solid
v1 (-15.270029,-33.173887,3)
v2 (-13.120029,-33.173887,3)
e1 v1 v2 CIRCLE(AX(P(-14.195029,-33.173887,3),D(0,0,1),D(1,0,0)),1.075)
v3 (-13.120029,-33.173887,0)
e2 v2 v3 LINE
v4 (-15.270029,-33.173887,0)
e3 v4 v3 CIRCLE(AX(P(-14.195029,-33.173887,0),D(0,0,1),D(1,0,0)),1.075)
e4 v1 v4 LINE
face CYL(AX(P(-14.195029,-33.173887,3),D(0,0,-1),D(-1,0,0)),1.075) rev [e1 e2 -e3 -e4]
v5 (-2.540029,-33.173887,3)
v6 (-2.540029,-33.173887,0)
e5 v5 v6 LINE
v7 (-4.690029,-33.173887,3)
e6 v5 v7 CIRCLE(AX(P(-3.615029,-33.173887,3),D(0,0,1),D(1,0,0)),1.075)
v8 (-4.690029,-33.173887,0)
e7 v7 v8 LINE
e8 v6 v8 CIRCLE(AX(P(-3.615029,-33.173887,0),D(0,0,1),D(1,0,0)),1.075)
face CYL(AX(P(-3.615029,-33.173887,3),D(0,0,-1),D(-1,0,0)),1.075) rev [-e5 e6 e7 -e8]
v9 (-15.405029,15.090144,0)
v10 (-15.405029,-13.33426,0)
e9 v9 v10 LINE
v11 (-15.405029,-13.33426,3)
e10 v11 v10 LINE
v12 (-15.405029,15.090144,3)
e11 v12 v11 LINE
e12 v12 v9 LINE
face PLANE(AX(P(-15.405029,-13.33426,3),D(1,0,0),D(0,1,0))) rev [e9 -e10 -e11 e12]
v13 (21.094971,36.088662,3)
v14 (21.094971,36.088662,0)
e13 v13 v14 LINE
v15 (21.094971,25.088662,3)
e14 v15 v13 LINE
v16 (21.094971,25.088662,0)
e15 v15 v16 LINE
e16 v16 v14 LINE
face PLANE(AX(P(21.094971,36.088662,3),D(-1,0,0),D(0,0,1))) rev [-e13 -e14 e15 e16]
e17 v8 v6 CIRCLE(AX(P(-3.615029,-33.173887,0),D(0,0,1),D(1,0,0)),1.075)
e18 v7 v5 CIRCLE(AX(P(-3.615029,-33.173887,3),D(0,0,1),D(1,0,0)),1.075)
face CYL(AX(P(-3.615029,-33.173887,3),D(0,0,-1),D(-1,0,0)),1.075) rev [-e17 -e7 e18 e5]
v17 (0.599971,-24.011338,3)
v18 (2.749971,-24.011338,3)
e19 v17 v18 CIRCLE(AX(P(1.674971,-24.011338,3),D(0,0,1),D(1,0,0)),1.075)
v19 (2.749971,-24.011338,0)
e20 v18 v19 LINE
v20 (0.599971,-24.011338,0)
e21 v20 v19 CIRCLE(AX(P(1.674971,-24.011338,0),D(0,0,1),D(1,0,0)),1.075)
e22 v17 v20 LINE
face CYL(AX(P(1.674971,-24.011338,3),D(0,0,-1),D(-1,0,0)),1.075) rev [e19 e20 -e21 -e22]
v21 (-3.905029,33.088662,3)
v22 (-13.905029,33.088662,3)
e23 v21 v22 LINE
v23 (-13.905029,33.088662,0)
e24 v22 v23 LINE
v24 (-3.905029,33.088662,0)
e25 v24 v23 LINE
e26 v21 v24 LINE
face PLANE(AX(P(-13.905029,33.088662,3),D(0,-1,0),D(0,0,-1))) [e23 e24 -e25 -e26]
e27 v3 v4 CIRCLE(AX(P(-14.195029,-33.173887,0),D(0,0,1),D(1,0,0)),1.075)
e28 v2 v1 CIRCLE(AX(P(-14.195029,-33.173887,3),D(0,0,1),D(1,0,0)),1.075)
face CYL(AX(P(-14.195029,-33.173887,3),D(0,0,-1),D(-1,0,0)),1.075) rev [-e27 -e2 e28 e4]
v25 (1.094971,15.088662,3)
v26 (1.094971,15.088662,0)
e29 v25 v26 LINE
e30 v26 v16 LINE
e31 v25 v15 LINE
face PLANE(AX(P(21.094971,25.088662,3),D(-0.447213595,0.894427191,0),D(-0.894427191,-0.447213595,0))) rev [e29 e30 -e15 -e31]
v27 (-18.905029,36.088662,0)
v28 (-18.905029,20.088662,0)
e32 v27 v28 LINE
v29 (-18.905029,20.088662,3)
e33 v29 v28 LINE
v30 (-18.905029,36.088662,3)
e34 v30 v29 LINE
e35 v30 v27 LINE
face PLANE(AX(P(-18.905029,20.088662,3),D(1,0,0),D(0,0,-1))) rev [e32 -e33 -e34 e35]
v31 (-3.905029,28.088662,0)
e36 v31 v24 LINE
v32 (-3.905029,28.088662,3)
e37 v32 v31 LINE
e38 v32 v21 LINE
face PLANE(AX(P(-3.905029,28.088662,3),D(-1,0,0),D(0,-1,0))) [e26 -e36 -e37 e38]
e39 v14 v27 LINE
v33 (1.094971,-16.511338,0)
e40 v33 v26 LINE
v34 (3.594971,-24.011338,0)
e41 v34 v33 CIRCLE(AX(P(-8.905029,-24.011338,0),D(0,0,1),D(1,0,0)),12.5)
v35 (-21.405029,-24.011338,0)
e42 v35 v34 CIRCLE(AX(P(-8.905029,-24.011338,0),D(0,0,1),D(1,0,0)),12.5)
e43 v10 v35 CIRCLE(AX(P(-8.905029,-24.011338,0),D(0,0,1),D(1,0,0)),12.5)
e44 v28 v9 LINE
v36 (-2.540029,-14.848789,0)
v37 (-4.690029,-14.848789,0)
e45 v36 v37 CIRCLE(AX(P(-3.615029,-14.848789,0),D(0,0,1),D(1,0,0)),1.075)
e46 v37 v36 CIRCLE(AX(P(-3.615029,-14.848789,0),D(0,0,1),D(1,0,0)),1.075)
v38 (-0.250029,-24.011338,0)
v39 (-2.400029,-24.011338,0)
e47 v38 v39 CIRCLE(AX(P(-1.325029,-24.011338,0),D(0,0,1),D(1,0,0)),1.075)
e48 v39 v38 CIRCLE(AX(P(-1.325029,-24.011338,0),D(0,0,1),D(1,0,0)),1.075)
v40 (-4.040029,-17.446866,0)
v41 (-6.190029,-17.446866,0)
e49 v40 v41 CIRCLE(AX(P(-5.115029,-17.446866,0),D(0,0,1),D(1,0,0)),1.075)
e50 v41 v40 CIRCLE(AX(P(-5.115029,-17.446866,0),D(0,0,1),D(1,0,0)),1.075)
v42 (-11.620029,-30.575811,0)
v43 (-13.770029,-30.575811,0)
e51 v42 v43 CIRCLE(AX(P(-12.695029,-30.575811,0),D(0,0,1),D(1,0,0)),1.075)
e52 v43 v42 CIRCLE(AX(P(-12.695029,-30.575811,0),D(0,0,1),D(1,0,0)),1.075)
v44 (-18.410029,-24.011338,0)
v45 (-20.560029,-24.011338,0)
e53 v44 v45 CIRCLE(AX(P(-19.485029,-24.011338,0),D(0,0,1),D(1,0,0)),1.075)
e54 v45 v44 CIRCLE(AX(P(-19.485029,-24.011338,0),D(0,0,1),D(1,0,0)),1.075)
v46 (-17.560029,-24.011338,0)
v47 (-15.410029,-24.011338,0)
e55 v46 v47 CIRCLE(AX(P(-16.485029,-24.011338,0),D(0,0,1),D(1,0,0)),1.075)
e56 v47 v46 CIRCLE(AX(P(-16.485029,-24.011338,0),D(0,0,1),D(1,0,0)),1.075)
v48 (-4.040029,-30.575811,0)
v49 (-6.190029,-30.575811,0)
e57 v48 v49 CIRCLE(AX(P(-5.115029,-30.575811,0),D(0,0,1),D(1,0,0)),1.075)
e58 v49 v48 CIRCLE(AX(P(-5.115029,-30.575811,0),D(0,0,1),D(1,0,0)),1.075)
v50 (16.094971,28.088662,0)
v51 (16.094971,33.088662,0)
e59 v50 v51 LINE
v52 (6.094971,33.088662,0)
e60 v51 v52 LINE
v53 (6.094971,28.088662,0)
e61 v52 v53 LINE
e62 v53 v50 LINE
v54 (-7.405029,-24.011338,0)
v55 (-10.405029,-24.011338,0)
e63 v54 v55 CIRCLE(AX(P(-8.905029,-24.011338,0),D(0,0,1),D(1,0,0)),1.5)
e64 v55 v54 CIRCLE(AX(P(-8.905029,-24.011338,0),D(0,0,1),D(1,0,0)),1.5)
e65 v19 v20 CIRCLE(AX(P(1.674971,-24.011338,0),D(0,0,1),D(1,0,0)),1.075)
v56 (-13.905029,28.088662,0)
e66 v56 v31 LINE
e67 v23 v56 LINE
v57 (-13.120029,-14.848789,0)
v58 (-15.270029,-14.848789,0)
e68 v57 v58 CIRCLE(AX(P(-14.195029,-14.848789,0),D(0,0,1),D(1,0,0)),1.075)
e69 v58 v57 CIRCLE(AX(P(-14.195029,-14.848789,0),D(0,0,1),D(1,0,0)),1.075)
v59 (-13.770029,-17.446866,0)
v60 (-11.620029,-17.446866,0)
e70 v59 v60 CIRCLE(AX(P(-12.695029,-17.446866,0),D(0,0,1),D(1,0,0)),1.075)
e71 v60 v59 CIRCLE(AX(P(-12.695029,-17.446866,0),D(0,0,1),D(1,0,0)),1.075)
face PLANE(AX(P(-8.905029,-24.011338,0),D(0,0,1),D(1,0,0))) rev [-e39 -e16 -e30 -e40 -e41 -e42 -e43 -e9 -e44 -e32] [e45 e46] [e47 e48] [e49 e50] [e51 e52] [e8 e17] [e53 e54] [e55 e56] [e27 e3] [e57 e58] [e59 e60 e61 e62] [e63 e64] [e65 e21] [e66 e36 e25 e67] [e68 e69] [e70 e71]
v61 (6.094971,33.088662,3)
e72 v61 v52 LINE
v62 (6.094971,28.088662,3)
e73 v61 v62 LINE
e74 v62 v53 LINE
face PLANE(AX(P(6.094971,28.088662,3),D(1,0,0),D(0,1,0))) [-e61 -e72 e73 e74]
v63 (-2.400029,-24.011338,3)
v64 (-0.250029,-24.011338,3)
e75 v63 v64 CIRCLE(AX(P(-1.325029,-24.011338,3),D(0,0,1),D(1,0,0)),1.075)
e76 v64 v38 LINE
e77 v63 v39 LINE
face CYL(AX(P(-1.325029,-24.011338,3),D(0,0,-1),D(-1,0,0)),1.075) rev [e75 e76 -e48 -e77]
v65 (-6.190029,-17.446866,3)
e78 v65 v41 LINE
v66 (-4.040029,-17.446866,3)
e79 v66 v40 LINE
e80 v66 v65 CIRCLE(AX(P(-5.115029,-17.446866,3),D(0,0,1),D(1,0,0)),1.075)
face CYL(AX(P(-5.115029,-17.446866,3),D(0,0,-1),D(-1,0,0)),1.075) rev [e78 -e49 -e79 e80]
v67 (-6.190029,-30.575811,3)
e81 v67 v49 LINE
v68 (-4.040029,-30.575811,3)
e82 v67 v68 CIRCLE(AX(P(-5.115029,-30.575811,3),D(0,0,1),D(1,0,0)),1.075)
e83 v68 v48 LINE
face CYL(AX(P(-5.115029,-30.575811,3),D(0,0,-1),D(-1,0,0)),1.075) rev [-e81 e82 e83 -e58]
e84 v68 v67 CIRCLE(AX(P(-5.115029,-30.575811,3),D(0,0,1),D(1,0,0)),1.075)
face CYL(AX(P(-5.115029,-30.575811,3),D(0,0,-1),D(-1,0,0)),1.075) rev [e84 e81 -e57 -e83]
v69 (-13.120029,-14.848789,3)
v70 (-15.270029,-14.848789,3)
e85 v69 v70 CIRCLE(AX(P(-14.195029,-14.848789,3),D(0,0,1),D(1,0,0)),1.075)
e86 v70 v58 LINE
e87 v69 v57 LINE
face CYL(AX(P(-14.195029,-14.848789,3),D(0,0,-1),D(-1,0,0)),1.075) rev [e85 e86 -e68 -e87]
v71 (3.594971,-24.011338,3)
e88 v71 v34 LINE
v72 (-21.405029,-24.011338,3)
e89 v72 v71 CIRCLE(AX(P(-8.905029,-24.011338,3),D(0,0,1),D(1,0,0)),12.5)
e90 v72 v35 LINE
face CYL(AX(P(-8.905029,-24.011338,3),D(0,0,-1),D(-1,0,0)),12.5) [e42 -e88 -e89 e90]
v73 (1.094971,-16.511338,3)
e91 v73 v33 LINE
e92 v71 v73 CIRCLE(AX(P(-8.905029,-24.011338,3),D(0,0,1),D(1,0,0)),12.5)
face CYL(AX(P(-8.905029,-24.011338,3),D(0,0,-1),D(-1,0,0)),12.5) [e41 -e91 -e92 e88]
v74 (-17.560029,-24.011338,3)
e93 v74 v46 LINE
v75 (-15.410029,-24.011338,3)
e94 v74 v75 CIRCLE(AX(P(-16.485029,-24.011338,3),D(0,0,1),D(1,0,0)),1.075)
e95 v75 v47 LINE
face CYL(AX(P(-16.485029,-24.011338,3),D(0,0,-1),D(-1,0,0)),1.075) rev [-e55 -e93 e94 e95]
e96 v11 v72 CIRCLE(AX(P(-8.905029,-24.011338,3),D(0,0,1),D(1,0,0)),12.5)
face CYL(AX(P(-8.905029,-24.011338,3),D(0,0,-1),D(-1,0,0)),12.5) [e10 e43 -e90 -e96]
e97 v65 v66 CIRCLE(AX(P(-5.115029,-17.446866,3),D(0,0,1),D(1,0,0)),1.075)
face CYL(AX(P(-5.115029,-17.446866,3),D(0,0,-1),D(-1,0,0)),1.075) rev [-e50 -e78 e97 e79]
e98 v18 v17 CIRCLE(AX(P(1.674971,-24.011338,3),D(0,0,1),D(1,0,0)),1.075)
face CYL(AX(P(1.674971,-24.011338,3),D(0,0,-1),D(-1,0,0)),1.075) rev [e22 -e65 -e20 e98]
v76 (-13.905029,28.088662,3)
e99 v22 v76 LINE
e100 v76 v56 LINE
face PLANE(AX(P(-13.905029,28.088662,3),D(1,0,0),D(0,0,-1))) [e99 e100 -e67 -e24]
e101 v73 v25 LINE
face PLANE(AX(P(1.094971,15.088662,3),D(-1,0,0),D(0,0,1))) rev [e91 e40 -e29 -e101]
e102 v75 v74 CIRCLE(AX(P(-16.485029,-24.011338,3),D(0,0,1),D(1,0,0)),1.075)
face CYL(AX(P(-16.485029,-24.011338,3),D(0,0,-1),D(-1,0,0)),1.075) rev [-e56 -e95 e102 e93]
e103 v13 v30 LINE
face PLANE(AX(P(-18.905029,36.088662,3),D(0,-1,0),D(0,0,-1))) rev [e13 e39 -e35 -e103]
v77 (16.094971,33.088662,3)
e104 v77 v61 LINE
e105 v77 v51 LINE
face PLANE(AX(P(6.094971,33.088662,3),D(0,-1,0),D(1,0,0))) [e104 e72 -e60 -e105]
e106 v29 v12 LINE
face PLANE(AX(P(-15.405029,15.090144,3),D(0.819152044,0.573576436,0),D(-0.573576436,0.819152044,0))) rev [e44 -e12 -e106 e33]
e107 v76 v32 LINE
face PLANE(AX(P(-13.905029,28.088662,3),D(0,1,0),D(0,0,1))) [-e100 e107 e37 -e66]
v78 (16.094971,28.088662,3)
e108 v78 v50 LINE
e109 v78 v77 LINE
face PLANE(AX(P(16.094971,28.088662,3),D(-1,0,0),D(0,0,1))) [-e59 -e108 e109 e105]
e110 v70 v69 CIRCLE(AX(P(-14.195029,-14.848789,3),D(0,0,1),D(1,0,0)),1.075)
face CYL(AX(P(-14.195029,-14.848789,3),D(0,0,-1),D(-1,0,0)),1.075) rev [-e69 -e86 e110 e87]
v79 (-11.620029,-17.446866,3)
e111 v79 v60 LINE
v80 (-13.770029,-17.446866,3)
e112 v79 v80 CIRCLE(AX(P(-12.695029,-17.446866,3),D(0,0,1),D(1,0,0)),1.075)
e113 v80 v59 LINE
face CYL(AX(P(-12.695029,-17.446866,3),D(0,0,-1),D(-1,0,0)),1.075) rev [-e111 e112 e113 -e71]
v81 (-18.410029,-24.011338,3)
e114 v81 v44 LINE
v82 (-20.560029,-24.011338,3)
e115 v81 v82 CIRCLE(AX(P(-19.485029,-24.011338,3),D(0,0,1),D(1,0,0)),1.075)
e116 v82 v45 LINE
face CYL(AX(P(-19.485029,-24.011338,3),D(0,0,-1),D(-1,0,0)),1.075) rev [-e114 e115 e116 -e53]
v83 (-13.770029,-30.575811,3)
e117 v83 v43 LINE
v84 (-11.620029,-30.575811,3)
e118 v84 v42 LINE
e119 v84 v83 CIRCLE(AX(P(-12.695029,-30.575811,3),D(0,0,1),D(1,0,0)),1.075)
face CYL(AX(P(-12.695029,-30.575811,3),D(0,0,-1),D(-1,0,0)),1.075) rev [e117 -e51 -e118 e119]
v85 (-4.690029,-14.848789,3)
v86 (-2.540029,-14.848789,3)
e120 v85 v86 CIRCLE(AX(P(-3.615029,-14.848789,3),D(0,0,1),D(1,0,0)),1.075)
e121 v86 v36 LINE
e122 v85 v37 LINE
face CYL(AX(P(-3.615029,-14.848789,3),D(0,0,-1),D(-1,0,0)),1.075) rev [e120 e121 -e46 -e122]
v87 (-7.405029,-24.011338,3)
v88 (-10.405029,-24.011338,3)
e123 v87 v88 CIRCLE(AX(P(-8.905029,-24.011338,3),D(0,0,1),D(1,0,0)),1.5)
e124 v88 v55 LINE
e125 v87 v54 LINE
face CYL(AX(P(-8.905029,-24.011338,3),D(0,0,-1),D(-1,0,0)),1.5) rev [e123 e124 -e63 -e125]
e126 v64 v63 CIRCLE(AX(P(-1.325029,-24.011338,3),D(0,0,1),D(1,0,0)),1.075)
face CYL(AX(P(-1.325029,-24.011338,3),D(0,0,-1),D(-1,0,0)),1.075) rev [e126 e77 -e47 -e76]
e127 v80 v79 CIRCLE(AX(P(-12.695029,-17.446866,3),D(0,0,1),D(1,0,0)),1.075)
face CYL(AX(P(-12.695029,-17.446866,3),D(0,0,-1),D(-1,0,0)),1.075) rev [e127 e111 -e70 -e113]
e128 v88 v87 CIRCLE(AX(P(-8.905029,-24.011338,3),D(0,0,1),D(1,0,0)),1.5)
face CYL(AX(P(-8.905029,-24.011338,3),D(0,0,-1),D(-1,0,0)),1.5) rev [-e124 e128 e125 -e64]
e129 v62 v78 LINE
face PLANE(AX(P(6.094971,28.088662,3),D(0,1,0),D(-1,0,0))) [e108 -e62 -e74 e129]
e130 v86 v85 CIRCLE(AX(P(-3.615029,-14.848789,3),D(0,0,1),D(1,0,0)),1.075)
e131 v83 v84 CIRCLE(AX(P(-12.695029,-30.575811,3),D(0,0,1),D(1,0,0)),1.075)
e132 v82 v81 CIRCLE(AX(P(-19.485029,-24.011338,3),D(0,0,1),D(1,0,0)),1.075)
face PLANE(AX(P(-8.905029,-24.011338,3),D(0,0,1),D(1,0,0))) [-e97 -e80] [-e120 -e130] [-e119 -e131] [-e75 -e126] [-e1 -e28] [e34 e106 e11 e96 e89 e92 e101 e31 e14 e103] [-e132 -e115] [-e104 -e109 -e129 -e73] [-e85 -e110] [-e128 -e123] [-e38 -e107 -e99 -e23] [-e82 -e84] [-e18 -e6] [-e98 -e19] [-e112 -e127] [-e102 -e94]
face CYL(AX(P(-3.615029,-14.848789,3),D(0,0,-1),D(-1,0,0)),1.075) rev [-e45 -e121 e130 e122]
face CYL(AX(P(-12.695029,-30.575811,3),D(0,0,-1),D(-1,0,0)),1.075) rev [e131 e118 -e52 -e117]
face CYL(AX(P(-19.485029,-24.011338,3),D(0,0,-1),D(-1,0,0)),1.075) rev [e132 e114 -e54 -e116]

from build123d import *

# Parameters (mm, degrees)
SKETCH_1_R      = 1.5
SKETCH_1_R_2    = 1.075
SKETCH_1_W      = 10
SKETCH_1_H      = 5
EXTRUDE_1_DEPTH = 3


with BuildPart() as part:
    # 草图1 → 凸台-拉伸1 (new body)
    with BuildSketch(Plane.XY):
        with BuildLine():
            Line((-15.405029449, -13.33425996), (-15.405029449, 15.090143764))
            Line((-15.405029449, 15.090143764), (-18.905029449, 20.088661788))
            Line((-18.905029449, 20.088661788), (-18.905029449, 36.088661788))
            Line((-18.905029449, 36.088661788), (21.094970551, 36.088661788))
            Line((21.094970551, 36.088661788), (21.094970551, 25.088661788))
            Line((21.094970551, 25.088661788), (1.094970551, 15.088661788))
            Line((1.094970551, 15.088661788), (1.094970551, -16.511338212))
            ThreePointArc((1.094970551, -16.511338212), (-11.26849228, -36.285866449), (-15.405029449, -13.33425996))
        make_face()
        with Locations((-8.905029449, -24.011338212)):
            Circle(SKETCH_1_R, mode=Mode.SUBTRACT)
        with Locations((-1.325029449, -24.011338212)):
            Circle(SKETCH_1_R_2, mode=Mode.SUBTRACT)
        with Locations((1.674970551, -24.011338212)):
            Circle(SKETCH_1_R_2, mode=Mode.SUBTRACT)
        with Locations((-5.115029449, -30.575810773)):
            Circle(SKETCH_1_R_2, mode=Mode.SUBTRACT)
        with Locations((-3.615029449, -33.173886984)):
            Circle(SKETCH_1_R_2, mode=Mode.SUBTRACT)
        with Locations((-12.695029449, -30.575810773)):
            Circle(SKETCH_1_R_2, mode=Mode.SUBTRACT)
        with Locations((-14.195029449, -33.173886984)):
            Circle(SKETCH_1_R_2, mode=Mode.SUBTRACT)
        with Locations((-16.485029449, -24.011338212)):
            Circle(SKETCH_1_R_2, mode=Mode.SUBTRACT)
        with Locations((-19.485029449, -24.011338212)):
            Circle(SKETCH_1_R_2, mode=Mode.SUBTRACT)
        with Locations((-12.695029449, -17.446865652)):
            Circle(SKETCH_1_R_2, mode=Mode.SUBTRACT)
        with Locations((-14.195029449, -14.84878944)):
            Circle(SKETCH_1_R_2, mode=Mode.SUBTRACT)
        with Locations((-5.115029449, -17.446865652)):
            Circle(SKETCH_1_R_2, mode=Mode.SUBTRACT)
        with Locations((-3.615029449, -14.84878944)):
            Circle(SKETCH_1_R_2, mode=Mode.SUBTRACT)
        with Locations((-8.905029449, 30.588661788)):
            Rectangle(SKETCH_1_W, SKETCH_1_H, mode=Mode.SUBTRACT)
        with Locations((11.094970551, 30.588661788)):
            Rectangle(SKETCH_1_W, SKETCH_1_H, mode=Mode.SUBTRACT)
    extrude(amount=EXTRUDE_1_DEPTH)


solid = part.part
